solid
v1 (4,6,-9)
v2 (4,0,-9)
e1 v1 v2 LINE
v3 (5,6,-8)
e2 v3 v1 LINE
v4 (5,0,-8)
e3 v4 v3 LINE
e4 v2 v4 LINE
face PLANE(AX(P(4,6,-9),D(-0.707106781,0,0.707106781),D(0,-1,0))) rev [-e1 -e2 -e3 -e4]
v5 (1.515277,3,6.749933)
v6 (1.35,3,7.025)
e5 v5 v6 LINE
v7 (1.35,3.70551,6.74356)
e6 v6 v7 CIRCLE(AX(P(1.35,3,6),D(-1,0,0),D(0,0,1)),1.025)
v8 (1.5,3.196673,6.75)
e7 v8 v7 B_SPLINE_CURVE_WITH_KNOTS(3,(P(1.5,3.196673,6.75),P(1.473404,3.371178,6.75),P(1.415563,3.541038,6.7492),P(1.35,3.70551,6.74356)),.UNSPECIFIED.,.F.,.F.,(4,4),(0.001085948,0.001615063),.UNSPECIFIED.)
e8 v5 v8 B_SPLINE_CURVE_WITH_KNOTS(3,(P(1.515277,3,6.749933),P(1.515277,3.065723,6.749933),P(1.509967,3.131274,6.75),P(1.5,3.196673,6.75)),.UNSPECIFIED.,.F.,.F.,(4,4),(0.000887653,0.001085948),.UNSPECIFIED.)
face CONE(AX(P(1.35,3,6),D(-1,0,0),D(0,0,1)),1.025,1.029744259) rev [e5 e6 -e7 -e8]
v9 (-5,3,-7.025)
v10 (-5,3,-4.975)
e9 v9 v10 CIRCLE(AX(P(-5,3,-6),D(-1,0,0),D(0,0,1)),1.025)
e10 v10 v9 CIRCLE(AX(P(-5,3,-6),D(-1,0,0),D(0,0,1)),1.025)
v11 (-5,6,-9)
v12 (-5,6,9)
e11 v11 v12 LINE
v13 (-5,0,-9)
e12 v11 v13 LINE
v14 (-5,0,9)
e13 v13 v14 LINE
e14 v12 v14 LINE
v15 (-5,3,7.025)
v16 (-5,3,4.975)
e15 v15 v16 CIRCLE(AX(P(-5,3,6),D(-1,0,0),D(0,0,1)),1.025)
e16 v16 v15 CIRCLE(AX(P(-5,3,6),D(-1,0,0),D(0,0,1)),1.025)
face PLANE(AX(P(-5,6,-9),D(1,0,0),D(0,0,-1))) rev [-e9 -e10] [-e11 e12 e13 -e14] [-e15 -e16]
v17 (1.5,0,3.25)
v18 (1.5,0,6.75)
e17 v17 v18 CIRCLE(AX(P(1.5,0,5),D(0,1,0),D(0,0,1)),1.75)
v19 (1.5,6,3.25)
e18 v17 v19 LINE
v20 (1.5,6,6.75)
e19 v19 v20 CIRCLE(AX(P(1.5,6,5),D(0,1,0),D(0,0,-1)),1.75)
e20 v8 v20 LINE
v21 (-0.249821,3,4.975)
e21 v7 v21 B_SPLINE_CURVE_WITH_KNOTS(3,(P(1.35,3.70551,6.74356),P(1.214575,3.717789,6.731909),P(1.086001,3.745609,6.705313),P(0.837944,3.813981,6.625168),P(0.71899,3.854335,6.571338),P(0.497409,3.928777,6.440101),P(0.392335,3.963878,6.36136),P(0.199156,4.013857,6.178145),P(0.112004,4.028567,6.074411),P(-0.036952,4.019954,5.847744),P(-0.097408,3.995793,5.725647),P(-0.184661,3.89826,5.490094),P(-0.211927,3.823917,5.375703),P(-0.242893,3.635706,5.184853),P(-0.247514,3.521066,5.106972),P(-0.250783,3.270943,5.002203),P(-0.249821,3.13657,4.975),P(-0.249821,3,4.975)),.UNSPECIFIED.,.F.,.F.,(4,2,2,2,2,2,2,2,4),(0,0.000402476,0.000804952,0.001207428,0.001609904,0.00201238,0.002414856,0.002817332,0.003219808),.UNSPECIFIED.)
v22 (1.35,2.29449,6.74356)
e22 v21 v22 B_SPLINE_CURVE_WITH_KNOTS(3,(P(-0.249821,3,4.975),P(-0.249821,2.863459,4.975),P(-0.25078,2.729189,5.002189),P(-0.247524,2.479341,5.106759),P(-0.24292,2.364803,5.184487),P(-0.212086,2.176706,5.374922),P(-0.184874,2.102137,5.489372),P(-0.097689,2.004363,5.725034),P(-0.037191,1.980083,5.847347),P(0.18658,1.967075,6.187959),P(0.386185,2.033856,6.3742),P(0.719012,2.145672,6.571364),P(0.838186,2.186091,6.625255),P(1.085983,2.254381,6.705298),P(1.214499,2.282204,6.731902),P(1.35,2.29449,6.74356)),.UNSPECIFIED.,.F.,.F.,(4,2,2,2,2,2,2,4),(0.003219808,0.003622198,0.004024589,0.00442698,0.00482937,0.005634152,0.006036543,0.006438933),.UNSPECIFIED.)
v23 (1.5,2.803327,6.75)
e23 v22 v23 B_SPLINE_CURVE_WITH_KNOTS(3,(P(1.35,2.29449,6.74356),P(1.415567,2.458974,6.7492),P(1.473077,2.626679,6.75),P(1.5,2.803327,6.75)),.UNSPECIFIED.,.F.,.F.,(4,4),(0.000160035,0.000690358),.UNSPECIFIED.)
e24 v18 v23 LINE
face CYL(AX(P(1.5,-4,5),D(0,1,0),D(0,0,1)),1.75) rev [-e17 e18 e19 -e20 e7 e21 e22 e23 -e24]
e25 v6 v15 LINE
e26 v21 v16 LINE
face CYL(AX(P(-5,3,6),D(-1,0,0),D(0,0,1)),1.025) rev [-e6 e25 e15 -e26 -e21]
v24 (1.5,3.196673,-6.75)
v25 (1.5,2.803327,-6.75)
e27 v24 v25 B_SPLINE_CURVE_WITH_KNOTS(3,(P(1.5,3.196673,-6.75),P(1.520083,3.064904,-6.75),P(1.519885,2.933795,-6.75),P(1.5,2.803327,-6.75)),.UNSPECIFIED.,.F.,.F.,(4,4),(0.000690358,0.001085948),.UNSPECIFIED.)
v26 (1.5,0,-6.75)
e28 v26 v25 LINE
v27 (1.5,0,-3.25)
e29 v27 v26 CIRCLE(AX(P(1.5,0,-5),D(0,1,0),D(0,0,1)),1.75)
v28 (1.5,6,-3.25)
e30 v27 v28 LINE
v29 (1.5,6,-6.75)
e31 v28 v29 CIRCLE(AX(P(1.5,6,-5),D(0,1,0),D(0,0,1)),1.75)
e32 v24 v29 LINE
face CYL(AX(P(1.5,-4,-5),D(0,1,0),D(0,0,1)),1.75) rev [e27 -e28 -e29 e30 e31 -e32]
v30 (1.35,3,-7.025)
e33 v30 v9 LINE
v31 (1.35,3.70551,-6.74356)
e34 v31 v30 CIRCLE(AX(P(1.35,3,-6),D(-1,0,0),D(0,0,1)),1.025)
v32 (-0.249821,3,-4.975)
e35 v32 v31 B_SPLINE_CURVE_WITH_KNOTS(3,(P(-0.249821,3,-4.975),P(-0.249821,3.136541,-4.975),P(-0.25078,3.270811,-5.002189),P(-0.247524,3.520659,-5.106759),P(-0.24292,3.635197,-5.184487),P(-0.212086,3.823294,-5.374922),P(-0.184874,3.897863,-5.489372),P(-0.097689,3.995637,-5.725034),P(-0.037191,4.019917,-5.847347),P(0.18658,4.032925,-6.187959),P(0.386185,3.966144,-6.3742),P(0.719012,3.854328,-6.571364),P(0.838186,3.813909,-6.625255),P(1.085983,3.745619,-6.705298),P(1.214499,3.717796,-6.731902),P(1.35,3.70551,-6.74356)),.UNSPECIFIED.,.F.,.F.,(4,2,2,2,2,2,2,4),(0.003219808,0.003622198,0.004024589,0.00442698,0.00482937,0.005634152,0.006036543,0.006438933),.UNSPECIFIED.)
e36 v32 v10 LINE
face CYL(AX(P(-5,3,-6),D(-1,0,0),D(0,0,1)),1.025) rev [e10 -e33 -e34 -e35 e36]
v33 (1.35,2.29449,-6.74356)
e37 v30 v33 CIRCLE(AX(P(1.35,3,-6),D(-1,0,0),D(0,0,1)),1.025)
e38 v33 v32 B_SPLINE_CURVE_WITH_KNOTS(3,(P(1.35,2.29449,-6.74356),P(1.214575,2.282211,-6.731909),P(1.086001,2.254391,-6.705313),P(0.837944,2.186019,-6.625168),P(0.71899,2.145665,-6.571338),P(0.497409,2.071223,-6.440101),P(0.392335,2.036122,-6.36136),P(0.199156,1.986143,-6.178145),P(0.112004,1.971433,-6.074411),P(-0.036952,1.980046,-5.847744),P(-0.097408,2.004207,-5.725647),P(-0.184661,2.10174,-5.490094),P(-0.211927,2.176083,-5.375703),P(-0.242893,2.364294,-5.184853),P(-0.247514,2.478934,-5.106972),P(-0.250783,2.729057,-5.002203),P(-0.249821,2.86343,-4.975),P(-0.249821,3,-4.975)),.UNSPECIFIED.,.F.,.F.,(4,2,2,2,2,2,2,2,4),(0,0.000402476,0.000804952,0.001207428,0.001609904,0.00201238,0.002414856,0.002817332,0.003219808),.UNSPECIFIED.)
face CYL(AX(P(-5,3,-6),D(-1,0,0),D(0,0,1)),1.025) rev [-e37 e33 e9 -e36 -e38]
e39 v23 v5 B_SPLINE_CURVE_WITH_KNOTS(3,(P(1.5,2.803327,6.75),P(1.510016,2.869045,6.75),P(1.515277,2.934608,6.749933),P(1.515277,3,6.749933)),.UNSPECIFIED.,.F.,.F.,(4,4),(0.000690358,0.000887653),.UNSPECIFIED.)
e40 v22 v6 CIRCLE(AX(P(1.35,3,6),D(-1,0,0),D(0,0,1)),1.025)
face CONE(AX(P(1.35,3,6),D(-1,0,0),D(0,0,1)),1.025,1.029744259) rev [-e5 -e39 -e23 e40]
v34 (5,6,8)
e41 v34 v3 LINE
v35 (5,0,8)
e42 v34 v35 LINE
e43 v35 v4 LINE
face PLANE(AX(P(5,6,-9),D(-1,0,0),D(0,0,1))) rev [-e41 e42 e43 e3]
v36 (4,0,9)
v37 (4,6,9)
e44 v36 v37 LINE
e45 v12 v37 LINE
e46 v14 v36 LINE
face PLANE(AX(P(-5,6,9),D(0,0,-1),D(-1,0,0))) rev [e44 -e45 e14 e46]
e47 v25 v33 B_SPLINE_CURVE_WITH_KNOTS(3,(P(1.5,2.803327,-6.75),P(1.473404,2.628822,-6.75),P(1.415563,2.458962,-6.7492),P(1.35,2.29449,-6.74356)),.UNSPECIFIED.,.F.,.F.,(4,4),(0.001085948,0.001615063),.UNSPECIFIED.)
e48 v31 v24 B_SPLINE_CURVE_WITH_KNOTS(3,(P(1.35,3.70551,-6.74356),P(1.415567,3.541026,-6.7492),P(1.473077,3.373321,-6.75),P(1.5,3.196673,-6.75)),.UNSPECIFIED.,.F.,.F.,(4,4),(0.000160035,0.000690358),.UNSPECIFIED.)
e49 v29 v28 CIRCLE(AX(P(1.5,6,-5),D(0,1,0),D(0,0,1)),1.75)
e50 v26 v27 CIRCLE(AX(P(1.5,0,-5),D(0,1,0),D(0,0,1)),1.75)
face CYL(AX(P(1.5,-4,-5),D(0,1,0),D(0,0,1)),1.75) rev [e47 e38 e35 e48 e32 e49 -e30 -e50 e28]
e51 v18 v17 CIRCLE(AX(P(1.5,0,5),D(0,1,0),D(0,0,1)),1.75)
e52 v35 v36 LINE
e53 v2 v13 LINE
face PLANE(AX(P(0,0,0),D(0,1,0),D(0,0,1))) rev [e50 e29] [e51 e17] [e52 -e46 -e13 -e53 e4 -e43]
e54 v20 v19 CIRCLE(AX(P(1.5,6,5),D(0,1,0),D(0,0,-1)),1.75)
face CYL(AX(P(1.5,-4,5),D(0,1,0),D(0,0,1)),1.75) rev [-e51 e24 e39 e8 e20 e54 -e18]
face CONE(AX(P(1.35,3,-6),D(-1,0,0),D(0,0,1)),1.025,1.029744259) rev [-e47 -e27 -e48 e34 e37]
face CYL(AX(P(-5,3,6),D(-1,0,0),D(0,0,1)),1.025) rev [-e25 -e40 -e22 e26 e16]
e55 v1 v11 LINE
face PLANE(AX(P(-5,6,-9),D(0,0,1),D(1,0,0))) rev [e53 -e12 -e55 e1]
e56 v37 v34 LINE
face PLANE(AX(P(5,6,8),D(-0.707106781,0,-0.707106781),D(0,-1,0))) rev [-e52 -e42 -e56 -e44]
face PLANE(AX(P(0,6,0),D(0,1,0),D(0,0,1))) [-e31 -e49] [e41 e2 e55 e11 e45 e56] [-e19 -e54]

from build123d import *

# Parameters (mm, degrees)
SKETCH1_W               = 10
SKETCH1_H               = 18
BOSS_EXTRUDE1_DEPTH     = 6
SKETCH2_R               = 1.75
CUT_EXTRUDE1_DEPTH      = 10
CHAMFER1_SIZE           = 1
M2_5_TAPPED_HOLE1_D     = 2.05
M2_5_TAPPED_HOLE1_DEPTH = 6.35
M2_5_TAPPED_HOLE1_TIP   = 0.615882135


with BuildPart() as part:
    # Sketch1 → Boss-Extrude1 (new body)
    with BuildSketch(Plane(origin=(0, 0, 0), x_dir=(1, 0, 0), z_dir=(0, 1, 0))):
        Rectangle(SKETCH1_W, SKETCH1_H)
    extrude(amount=BOSS_EXTRUDE1_DEPTH)

    # Sketch2 → Cut-Extrude1 (cut)
    with BuildSketch(Plane(origin=(0, 6, 0), x_dir=(1, 0, 0), z_dir=(0, 1, 0))):
        with Locations(Location((1.5, 5, 0), (0, 0, 270))):
            Circle(SKETCH2_R)
        with Locations(Location((1.5, -5, 0), (0, 0, 270))):
            Circle(SKETCH2_R)
    extrude(amount=-CUT_EXTRUDE1_DEPTH, mode=Mode.SUBTRACT)

    # Chamfer1
    chamfer1_edges = [part.edges().sort_by_distance(p)[0] for p in [
        (5, 3, 9),
        (5, 3, -9),
    ]]
    chamfer(chamfer1_edges, length=CHAMFER1_SIZE)

    # M2.5 Tapped Hole1
    with Locations(Plane(origin=(-5, 3, -6), x_dir=(0, 0, -1), z_dir=(-1, 0, 0))):
        with Locations((0, 0), (-12, 0)):
            Hole(M2_5_TAPPED_HOLE1_D / 2, depth=M2_5_TAPPED_HOLE1_DEPTH)
            with Locations((0, 0, -(M2_5_TAPPED_HOLE1_DEPTH + M2_5_TAPPED_HOLE1_TIP / 2))):  # 118° drill point
                Cone(0, M2_5_TAPPED_HOLE1_D / 2, M2_5_TAPPED_HOLE1_TIP, mode=Mode.SUBTRACT)


solid = part.part
